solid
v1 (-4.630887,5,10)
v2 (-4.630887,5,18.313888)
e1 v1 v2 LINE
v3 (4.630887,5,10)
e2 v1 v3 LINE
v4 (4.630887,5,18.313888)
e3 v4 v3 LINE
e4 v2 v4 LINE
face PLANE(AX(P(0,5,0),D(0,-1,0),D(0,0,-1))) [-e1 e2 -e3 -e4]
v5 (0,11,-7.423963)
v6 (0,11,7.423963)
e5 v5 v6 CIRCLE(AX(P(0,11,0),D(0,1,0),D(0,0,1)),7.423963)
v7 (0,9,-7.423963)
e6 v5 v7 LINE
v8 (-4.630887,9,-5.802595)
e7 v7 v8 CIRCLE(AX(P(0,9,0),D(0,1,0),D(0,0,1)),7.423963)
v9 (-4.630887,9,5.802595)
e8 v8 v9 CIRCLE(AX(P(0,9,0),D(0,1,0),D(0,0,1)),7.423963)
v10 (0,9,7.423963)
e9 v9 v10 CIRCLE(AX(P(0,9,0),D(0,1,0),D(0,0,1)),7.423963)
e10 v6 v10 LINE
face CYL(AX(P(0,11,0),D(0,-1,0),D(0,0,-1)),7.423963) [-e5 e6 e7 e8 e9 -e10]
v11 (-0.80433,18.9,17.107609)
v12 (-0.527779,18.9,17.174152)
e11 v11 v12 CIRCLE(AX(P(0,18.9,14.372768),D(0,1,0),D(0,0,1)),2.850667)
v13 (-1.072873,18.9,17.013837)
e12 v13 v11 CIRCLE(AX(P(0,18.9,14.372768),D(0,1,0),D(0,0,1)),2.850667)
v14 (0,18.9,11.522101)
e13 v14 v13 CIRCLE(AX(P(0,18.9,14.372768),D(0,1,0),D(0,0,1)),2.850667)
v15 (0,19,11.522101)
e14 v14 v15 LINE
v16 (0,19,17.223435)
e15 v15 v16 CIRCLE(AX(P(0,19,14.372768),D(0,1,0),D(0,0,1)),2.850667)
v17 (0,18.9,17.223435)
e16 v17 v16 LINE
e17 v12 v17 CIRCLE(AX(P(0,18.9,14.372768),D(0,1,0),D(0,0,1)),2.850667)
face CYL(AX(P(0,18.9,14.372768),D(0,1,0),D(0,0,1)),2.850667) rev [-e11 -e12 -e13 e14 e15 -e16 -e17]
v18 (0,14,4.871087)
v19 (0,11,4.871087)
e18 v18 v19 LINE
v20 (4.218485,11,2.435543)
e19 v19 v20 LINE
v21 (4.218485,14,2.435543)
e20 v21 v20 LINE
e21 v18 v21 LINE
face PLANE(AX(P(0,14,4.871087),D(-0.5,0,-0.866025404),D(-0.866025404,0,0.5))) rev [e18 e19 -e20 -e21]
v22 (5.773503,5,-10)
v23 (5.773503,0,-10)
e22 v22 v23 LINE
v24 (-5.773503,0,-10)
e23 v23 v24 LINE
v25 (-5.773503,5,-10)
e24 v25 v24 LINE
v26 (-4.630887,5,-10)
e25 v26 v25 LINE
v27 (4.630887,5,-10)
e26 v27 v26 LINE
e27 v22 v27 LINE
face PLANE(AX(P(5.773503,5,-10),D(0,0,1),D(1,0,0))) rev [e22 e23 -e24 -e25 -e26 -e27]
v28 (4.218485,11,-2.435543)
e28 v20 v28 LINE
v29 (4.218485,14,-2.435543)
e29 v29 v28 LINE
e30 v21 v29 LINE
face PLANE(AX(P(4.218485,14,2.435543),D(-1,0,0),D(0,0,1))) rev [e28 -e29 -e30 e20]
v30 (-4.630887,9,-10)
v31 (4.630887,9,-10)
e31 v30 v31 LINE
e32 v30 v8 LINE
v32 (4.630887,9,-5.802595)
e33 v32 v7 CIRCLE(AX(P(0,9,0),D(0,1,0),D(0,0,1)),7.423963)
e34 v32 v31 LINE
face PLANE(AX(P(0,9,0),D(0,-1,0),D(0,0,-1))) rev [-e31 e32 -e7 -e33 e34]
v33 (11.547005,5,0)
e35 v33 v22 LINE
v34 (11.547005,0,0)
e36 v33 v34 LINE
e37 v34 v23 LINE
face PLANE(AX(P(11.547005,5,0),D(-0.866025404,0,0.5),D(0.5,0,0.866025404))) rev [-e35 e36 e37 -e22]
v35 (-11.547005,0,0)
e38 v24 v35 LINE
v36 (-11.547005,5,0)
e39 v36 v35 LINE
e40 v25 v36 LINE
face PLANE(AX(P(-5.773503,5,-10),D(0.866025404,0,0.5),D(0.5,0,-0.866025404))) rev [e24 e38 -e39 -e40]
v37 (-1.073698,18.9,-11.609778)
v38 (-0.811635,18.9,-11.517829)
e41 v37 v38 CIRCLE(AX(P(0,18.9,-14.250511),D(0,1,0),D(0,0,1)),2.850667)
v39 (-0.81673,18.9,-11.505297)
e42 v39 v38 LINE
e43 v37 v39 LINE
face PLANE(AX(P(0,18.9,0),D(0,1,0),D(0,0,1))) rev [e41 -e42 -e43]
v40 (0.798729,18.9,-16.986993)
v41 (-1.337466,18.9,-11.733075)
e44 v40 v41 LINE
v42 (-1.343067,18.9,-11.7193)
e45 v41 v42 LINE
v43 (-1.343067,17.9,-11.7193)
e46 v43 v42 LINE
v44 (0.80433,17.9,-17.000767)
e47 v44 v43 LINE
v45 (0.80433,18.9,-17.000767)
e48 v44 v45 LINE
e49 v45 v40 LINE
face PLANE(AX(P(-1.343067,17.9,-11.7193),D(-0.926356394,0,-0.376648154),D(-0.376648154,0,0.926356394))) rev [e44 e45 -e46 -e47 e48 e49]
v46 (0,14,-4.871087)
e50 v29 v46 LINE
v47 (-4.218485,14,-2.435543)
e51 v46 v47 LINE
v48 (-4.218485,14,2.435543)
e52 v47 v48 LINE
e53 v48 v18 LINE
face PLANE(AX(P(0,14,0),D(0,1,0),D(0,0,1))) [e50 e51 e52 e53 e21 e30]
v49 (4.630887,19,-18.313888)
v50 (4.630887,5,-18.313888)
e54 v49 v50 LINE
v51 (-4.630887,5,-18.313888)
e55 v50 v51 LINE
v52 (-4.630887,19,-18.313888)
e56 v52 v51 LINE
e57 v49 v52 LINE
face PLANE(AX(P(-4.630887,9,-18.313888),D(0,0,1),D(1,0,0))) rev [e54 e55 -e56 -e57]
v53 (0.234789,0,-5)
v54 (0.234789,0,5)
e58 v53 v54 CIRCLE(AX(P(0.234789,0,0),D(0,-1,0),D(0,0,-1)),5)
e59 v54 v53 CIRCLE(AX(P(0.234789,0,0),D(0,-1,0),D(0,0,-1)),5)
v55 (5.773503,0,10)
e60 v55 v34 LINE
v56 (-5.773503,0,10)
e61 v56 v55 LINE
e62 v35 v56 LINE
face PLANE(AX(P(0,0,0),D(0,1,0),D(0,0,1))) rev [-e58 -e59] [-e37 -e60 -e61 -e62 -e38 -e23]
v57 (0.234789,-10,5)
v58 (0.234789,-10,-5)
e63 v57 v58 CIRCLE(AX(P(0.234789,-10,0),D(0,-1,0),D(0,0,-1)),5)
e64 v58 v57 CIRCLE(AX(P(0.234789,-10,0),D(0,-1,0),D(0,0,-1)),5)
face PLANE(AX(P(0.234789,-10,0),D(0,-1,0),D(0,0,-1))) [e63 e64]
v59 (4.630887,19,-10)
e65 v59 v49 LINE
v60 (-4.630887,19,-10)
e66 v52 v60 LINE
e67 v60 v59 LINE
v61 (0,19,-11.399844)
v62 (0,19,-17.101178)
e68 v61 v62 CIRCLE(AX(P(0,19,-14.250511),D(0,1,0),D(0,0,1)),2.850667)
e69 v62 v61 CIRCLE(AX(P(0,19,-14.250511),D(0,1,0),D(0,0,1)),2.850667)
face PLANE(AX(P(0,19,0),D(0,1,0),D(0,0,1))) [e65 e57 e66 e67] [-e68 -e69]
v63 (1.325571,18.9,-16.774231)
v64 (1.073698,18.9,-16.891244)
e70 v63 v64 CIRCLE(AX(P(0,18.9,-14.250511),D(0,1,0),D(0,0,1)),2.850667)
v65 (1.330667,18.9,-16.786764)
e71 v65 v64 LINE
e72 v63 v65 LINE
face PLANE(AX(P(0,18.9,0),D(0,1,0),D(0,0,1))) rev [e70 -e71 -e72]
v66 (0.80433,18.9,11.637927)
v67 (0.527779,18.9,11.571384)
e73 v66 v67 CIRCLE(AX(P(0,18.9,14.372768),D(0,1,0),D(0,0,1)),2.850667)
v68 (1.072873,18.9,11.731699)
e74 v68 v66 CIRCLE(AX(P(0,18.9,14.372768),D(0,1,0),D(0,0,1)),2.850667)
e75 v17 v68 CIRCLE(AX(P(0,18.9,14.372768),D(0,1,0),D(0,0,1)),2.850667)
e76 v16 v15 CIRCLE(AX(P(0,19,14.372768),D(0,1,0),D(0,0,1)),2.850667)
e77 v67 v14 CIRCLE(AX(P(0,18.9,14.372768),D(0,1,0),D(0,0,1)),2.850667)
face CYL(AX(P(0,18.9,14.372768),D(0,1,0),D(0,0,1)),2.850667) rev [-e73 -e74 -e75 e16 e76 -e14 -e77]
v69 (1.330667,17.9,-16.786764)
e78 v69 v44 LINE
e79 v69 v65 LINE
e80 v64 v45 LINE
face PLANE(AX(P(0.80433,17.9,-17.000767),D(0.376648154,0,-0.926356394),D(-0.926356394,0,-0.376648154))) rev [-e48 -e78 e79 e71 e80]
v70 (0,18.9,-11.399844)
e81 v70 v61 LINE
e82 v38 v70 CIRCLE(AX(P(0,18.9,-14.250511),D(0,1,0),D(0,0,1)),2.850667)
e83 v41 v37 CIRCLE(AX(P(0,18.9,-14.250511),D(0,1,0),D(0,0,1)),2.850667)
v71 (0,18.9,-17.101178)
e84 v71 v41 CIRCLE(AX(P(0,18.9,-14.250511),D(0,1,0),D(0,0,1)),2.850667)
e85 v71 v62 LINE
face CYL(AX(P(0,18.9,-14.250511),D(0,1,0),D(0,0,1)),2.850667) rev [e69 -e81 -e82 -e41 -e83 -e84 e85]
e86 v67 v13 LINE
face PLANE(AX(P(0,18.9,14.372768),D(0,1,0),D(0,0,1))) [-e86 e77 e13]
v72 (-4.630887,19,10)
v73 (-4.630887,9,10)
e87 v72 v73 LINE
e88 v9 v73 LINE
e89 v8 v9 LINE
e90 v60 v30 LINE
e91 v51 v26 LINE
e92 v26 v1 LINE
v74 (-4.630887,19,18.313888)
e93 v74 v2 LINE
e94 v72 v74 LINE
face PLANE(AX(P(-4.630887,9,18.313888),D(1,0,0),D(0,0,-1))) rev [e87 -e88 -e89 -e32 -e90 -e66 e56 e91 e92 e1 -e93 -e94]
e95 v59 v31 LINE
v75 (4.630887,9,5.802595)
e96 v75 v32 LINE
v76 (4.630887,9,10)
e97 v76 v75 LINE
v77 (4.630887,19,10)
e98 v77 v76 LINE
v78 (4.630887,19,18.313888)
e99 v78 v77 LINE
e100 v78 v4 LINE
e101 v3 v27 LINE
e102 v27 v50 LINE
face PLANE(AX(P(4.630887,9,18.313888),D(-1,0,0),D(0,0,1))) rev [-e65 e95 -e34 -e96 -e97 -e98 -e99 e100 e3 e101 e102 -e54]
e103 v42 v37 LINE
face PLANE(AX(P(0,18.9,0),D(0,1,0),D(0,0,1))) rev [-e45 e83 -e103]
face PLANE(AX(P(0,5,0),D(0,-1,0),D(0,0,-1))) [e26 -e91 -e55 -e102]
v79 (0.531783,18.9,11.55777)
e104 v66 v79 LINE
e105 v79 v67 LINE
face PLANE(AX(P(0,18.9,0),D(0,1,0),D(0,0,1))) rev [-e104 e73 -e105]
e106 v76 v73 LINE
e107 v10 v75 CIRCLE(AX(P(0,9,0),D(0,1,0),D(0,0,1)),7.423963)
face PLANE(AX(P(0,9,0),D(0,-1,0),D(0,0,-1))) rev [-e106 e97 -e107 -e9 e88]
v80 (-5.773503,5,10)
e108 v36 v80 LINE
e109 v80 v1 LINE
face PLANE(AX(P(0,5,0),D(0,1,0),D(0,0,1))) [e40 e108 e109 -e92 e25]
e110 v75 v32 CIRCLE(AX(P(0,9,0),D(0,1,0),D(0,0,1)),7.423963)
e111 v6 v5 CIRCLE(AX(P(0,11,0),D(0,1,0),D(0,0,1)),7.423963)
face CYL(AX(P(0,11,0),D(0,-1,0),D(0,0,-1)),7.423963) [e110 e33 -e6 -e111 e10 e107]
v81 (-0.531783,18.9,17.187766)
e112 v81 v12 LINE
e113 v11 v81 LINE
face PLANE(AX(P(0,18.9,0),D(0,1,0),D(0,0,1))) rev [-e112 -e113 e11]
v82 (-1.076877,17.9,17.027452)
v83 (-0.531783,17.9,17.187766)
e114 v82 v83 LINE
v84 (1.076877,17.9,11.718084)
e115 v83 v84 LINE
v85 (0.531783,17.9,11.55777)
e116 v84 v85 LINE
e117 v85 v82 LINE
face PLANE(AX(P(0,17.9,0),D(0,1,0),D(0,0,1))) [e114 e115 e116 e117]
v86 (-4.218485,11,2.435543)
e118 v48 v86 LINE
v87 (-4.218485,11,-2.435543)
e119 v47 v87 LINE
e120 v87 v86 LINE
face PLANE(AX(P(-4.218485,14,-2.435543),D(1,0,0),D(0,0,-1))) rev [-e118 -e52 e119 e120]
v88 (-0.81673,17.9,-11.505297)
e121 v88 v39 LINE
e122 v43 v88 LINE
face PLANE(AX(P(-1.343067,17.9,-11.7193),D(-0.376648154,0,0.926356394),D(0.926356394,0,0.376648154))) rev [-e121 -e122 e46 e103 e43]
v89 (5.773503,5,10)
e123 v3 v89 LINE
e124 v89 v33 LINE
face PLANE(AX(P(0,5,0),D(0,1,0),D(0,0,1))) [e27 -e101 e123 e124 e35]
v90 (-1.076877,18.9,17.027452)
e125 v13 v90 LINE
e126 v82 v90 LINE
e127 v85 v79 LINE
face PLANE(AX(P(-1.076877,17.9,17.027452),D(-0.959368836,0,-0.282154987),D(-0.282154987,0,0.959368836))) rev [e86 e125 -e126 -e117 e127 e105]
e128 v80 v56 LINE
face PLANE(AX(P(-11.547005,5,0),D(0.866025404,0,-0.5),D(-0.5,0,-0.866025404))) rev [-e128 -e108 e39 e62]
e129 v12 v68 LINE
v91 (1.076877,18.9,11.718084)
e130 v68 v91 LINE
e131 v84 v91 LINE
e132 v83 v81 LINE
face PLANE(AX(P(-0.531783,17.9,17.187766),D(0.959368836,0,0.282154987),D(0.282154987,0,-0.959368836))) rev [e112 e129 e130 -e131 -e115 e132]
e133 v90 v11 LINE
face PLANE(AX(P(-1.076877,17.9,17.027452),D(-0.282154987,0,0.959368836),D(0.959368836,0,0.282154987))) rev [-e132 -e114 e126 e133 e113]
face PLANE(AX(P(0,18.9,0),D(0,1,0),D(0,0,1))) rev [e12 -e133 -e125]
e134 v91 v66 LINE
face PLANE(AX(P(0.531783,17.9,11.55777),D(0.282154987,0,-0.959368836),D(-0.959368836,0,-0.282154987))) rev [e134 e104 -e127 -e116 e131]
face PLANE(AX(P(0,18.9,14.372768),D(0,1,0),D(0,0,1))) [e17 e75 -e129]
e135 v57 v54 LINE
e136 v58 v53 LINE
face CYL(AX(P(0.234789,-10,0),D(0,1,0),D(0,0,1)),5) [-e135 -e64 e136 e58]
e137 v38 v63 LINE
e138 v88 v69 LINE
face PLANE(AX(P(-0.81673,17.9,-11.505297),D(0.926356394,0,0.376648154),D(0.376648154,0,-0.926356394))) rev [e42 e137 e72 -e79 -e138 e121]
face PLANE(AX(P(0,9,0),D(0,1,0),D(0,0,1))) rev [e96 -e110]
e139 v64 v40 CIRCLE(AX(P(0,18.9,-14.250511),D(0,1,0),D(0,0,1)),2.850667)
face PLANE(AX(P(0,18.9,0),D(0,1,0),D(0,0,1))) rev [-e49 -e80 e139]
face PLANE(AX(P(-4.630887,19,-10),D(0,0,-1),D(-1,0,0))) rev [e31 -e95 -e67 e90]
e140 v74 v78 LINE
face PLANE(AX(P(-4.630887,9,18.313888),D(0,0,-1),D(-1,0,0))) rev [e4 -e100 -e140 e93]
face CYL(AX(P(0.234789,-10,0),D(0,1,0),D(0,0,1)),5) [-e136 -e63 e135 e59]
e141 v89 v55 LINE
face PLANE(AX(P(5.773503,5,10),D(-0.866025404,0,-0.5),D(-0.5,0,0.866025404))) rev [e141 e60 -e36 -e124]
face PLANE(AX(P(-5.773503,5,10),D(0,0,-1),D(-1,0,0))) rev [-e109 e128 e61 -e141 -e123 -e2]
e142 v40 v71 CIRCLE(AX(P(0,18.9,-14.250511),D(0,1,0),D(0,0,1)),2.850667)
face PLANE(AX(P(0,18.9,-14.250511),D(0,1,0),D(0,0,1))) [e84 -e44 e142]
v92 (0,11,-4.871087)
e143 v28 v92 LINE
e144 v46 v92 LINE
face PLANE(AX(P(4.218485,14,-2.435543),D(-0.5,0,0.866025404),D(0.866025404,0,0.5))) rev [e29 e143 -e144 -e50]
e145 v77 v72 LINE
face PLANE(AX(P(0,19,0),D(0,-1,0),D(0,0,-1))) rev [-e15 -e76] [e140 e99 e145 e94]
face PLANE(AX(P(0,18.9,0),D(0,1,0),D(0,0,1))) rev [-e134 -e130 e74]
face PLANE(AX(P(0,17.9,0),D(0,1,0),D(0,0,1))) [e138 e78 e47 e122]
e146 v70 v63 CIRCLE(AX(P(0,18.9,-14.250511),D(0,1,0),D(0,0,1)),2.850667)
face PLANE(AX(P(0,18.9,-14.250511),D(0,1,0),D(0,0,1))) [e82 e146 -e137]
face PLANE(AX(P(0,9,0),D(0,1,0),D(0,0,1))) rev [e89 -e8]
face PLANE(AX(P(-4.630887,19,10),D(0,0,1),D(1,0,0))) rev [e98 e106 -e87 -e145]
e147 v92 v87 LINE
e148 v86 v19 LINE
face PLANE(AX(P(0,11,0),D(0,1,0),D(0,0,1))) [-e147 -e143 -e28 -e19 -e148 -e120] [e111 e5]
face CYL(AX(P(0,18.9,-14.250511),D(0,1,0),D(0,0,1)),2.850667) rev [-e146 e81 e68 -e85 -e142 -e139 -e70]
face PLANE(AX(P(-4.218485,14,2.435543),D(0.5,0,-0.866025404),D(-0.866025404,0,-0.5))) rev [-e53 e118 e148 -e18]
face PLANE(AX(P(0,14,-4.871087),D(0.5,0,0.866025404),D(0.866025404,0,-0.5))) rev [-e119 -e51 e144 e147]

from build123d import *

# Parameters (mm, degrees)
BOSS_EXTRUDE1_DEPTH = 5
SKETCH2_R           = 5
BOSS_EXTRUDE2_DEPTH = 10
SKETCH3_W           = 9.261773254
SKETCH3_H           = 36.627775898
BOSS_EXTRUDE3_DEPTH = 4
SKETCH4_W           = 9.261773254
SKETCH4_H           = 8.313887949
BOSS_EXTRUDE4_DEPTH = 10
SKETCH5_R           = 7.423962758
BOSS_EXTRUDE5_DEPTH = 2
BOSS_EXTRUDE6_DEPTH = 3
SKETCH7_R           = 2.850666807
CUT_EXTRUDE1_DEPTH  = 0.1
CUT_EXTRUDE2_DEPTH  = 1


with BuildPart() as part:
    # Sketch1 → Boss-Extrude1 (new body)
    with BuildSketch(Plane(origin=(0, 0, 0), x_dir=(1, 0, 0), z_dir=(0, 1, 0))):
        Polygon((5.773502692, 10), (-5.773502692, 10), (-11.547005384, 0), (-5.773502692, -10), (5.773502692, -10), (11.547005384, 0), align=None)
    extrude(amount=BOSS_EXTRUDE1_DEPTH)

    # Sketch2 → Boss-Extrude2 (add)
    with BuildSketch(Plane.XZ):
        with Locations(Location((0.234789437, 0, 0), (0, 0, 270))):
            Circle(SKETCH2_R)
    extrude(amount=BOSS_EXTRUDE2_DEPTH)

    # Sketch3 → Boss-Extrude3 (add)
    with BuildSketch(Plane(origin=(0, 5, 0), x_dir=(1, 0, 0), z_dir=(0, 1, 0))):
        Rectangle(SKETCH3_W, SKETCH3_H)
    extrude(amount=BOSS_EXTRUDE3_DEPTH)

    # Sketch4 → Boss-Extrude4 (add)
    with BuildSketch(Plane(origin=(0, 9, 0), x_dir=(1, 0, 0), z_dir=(0, 1, 0))):
        with Locations((0, 14.156943975)):
            Rectangle(SKETCH4_W, SKETCH4_H)
        with Locations((0, -14.156943975)):
            Rectangle(SKETCH4_W, SKETCH4_H)
    extrude(amount=BOSS_EXTRUDE4_DEPTH)

    # Sketch5 → Boss-Extrude5 (add)
    with BuildSketch(Plane(origin=(0, 9, 0), x_dir=(1, 0, 0), z_dir=(0, 1, 0))):
        with Locations(Location((0, 0, 0), (0, 0, 51.407625877))):
            Circle(SKETCH5_R)
    extrude(amount=BOSS_EXTRUDE5_DEPTH)

    # Sketch6 → Boss-Extrude6 (add)
    with BuildSketch(Plane(origin=(0, 11, 0), x_dir=(1, 0, 0), z_dir=(0, 1, 0))):
        Polygon((0, 4.871086868), (-4.218484972, 2.435543434), (-4.218484972, -2.435543434), (0, -4.871086868), (4.218484972, -2.435543434), (4.218484972, 2.435543434), align=None)
    extrude(amount=BOSS_EXTRUDE6_DEPTH)

    # Sketch7 → Cut-Extrude1 (cut)
    with BuildSketch(Plane(origin=(0, 19, 0), x_dir=(1, 0, 0), z_dir=(0, 1, 0))):
        with Locations(Location((0, 14.250511049, 0), (0, 0, 270))):
            Circle(SKETCH7_R)
        with Locations(Location((0, -14.372767949, 0), (0, 0, 270))):
            Circle(SKETCH7_R)
    extrude(amount=-CUT_EXTRUDE1_DEPTH, mode=Mode.SUBTRACT)

    # Sketch8 → Cut-Extrude2 (cut)
    with BuildSketch(Plane(origin=(0, 18.9, 0), x_dir=(1, 0, 0), z_dir=(0, 1, 0))):
        Polygon((-1.343066927, 11.719300444), (0.804329856, 17.000767289), (1.330666503, 16.786763555), (-0.81673028, 11.505296711), align=None)
        Polygon((-1.076876675, -17.027451515), (0.531783037, -11.557769723), (1.076876675, -11.718084383), (-0.531783037, -17.187766175), align=None)
    extrude(amount=-CUT_EXTRUDE2_DEPTH, mode=Mode.SUBTRACT)


solid = part.part
